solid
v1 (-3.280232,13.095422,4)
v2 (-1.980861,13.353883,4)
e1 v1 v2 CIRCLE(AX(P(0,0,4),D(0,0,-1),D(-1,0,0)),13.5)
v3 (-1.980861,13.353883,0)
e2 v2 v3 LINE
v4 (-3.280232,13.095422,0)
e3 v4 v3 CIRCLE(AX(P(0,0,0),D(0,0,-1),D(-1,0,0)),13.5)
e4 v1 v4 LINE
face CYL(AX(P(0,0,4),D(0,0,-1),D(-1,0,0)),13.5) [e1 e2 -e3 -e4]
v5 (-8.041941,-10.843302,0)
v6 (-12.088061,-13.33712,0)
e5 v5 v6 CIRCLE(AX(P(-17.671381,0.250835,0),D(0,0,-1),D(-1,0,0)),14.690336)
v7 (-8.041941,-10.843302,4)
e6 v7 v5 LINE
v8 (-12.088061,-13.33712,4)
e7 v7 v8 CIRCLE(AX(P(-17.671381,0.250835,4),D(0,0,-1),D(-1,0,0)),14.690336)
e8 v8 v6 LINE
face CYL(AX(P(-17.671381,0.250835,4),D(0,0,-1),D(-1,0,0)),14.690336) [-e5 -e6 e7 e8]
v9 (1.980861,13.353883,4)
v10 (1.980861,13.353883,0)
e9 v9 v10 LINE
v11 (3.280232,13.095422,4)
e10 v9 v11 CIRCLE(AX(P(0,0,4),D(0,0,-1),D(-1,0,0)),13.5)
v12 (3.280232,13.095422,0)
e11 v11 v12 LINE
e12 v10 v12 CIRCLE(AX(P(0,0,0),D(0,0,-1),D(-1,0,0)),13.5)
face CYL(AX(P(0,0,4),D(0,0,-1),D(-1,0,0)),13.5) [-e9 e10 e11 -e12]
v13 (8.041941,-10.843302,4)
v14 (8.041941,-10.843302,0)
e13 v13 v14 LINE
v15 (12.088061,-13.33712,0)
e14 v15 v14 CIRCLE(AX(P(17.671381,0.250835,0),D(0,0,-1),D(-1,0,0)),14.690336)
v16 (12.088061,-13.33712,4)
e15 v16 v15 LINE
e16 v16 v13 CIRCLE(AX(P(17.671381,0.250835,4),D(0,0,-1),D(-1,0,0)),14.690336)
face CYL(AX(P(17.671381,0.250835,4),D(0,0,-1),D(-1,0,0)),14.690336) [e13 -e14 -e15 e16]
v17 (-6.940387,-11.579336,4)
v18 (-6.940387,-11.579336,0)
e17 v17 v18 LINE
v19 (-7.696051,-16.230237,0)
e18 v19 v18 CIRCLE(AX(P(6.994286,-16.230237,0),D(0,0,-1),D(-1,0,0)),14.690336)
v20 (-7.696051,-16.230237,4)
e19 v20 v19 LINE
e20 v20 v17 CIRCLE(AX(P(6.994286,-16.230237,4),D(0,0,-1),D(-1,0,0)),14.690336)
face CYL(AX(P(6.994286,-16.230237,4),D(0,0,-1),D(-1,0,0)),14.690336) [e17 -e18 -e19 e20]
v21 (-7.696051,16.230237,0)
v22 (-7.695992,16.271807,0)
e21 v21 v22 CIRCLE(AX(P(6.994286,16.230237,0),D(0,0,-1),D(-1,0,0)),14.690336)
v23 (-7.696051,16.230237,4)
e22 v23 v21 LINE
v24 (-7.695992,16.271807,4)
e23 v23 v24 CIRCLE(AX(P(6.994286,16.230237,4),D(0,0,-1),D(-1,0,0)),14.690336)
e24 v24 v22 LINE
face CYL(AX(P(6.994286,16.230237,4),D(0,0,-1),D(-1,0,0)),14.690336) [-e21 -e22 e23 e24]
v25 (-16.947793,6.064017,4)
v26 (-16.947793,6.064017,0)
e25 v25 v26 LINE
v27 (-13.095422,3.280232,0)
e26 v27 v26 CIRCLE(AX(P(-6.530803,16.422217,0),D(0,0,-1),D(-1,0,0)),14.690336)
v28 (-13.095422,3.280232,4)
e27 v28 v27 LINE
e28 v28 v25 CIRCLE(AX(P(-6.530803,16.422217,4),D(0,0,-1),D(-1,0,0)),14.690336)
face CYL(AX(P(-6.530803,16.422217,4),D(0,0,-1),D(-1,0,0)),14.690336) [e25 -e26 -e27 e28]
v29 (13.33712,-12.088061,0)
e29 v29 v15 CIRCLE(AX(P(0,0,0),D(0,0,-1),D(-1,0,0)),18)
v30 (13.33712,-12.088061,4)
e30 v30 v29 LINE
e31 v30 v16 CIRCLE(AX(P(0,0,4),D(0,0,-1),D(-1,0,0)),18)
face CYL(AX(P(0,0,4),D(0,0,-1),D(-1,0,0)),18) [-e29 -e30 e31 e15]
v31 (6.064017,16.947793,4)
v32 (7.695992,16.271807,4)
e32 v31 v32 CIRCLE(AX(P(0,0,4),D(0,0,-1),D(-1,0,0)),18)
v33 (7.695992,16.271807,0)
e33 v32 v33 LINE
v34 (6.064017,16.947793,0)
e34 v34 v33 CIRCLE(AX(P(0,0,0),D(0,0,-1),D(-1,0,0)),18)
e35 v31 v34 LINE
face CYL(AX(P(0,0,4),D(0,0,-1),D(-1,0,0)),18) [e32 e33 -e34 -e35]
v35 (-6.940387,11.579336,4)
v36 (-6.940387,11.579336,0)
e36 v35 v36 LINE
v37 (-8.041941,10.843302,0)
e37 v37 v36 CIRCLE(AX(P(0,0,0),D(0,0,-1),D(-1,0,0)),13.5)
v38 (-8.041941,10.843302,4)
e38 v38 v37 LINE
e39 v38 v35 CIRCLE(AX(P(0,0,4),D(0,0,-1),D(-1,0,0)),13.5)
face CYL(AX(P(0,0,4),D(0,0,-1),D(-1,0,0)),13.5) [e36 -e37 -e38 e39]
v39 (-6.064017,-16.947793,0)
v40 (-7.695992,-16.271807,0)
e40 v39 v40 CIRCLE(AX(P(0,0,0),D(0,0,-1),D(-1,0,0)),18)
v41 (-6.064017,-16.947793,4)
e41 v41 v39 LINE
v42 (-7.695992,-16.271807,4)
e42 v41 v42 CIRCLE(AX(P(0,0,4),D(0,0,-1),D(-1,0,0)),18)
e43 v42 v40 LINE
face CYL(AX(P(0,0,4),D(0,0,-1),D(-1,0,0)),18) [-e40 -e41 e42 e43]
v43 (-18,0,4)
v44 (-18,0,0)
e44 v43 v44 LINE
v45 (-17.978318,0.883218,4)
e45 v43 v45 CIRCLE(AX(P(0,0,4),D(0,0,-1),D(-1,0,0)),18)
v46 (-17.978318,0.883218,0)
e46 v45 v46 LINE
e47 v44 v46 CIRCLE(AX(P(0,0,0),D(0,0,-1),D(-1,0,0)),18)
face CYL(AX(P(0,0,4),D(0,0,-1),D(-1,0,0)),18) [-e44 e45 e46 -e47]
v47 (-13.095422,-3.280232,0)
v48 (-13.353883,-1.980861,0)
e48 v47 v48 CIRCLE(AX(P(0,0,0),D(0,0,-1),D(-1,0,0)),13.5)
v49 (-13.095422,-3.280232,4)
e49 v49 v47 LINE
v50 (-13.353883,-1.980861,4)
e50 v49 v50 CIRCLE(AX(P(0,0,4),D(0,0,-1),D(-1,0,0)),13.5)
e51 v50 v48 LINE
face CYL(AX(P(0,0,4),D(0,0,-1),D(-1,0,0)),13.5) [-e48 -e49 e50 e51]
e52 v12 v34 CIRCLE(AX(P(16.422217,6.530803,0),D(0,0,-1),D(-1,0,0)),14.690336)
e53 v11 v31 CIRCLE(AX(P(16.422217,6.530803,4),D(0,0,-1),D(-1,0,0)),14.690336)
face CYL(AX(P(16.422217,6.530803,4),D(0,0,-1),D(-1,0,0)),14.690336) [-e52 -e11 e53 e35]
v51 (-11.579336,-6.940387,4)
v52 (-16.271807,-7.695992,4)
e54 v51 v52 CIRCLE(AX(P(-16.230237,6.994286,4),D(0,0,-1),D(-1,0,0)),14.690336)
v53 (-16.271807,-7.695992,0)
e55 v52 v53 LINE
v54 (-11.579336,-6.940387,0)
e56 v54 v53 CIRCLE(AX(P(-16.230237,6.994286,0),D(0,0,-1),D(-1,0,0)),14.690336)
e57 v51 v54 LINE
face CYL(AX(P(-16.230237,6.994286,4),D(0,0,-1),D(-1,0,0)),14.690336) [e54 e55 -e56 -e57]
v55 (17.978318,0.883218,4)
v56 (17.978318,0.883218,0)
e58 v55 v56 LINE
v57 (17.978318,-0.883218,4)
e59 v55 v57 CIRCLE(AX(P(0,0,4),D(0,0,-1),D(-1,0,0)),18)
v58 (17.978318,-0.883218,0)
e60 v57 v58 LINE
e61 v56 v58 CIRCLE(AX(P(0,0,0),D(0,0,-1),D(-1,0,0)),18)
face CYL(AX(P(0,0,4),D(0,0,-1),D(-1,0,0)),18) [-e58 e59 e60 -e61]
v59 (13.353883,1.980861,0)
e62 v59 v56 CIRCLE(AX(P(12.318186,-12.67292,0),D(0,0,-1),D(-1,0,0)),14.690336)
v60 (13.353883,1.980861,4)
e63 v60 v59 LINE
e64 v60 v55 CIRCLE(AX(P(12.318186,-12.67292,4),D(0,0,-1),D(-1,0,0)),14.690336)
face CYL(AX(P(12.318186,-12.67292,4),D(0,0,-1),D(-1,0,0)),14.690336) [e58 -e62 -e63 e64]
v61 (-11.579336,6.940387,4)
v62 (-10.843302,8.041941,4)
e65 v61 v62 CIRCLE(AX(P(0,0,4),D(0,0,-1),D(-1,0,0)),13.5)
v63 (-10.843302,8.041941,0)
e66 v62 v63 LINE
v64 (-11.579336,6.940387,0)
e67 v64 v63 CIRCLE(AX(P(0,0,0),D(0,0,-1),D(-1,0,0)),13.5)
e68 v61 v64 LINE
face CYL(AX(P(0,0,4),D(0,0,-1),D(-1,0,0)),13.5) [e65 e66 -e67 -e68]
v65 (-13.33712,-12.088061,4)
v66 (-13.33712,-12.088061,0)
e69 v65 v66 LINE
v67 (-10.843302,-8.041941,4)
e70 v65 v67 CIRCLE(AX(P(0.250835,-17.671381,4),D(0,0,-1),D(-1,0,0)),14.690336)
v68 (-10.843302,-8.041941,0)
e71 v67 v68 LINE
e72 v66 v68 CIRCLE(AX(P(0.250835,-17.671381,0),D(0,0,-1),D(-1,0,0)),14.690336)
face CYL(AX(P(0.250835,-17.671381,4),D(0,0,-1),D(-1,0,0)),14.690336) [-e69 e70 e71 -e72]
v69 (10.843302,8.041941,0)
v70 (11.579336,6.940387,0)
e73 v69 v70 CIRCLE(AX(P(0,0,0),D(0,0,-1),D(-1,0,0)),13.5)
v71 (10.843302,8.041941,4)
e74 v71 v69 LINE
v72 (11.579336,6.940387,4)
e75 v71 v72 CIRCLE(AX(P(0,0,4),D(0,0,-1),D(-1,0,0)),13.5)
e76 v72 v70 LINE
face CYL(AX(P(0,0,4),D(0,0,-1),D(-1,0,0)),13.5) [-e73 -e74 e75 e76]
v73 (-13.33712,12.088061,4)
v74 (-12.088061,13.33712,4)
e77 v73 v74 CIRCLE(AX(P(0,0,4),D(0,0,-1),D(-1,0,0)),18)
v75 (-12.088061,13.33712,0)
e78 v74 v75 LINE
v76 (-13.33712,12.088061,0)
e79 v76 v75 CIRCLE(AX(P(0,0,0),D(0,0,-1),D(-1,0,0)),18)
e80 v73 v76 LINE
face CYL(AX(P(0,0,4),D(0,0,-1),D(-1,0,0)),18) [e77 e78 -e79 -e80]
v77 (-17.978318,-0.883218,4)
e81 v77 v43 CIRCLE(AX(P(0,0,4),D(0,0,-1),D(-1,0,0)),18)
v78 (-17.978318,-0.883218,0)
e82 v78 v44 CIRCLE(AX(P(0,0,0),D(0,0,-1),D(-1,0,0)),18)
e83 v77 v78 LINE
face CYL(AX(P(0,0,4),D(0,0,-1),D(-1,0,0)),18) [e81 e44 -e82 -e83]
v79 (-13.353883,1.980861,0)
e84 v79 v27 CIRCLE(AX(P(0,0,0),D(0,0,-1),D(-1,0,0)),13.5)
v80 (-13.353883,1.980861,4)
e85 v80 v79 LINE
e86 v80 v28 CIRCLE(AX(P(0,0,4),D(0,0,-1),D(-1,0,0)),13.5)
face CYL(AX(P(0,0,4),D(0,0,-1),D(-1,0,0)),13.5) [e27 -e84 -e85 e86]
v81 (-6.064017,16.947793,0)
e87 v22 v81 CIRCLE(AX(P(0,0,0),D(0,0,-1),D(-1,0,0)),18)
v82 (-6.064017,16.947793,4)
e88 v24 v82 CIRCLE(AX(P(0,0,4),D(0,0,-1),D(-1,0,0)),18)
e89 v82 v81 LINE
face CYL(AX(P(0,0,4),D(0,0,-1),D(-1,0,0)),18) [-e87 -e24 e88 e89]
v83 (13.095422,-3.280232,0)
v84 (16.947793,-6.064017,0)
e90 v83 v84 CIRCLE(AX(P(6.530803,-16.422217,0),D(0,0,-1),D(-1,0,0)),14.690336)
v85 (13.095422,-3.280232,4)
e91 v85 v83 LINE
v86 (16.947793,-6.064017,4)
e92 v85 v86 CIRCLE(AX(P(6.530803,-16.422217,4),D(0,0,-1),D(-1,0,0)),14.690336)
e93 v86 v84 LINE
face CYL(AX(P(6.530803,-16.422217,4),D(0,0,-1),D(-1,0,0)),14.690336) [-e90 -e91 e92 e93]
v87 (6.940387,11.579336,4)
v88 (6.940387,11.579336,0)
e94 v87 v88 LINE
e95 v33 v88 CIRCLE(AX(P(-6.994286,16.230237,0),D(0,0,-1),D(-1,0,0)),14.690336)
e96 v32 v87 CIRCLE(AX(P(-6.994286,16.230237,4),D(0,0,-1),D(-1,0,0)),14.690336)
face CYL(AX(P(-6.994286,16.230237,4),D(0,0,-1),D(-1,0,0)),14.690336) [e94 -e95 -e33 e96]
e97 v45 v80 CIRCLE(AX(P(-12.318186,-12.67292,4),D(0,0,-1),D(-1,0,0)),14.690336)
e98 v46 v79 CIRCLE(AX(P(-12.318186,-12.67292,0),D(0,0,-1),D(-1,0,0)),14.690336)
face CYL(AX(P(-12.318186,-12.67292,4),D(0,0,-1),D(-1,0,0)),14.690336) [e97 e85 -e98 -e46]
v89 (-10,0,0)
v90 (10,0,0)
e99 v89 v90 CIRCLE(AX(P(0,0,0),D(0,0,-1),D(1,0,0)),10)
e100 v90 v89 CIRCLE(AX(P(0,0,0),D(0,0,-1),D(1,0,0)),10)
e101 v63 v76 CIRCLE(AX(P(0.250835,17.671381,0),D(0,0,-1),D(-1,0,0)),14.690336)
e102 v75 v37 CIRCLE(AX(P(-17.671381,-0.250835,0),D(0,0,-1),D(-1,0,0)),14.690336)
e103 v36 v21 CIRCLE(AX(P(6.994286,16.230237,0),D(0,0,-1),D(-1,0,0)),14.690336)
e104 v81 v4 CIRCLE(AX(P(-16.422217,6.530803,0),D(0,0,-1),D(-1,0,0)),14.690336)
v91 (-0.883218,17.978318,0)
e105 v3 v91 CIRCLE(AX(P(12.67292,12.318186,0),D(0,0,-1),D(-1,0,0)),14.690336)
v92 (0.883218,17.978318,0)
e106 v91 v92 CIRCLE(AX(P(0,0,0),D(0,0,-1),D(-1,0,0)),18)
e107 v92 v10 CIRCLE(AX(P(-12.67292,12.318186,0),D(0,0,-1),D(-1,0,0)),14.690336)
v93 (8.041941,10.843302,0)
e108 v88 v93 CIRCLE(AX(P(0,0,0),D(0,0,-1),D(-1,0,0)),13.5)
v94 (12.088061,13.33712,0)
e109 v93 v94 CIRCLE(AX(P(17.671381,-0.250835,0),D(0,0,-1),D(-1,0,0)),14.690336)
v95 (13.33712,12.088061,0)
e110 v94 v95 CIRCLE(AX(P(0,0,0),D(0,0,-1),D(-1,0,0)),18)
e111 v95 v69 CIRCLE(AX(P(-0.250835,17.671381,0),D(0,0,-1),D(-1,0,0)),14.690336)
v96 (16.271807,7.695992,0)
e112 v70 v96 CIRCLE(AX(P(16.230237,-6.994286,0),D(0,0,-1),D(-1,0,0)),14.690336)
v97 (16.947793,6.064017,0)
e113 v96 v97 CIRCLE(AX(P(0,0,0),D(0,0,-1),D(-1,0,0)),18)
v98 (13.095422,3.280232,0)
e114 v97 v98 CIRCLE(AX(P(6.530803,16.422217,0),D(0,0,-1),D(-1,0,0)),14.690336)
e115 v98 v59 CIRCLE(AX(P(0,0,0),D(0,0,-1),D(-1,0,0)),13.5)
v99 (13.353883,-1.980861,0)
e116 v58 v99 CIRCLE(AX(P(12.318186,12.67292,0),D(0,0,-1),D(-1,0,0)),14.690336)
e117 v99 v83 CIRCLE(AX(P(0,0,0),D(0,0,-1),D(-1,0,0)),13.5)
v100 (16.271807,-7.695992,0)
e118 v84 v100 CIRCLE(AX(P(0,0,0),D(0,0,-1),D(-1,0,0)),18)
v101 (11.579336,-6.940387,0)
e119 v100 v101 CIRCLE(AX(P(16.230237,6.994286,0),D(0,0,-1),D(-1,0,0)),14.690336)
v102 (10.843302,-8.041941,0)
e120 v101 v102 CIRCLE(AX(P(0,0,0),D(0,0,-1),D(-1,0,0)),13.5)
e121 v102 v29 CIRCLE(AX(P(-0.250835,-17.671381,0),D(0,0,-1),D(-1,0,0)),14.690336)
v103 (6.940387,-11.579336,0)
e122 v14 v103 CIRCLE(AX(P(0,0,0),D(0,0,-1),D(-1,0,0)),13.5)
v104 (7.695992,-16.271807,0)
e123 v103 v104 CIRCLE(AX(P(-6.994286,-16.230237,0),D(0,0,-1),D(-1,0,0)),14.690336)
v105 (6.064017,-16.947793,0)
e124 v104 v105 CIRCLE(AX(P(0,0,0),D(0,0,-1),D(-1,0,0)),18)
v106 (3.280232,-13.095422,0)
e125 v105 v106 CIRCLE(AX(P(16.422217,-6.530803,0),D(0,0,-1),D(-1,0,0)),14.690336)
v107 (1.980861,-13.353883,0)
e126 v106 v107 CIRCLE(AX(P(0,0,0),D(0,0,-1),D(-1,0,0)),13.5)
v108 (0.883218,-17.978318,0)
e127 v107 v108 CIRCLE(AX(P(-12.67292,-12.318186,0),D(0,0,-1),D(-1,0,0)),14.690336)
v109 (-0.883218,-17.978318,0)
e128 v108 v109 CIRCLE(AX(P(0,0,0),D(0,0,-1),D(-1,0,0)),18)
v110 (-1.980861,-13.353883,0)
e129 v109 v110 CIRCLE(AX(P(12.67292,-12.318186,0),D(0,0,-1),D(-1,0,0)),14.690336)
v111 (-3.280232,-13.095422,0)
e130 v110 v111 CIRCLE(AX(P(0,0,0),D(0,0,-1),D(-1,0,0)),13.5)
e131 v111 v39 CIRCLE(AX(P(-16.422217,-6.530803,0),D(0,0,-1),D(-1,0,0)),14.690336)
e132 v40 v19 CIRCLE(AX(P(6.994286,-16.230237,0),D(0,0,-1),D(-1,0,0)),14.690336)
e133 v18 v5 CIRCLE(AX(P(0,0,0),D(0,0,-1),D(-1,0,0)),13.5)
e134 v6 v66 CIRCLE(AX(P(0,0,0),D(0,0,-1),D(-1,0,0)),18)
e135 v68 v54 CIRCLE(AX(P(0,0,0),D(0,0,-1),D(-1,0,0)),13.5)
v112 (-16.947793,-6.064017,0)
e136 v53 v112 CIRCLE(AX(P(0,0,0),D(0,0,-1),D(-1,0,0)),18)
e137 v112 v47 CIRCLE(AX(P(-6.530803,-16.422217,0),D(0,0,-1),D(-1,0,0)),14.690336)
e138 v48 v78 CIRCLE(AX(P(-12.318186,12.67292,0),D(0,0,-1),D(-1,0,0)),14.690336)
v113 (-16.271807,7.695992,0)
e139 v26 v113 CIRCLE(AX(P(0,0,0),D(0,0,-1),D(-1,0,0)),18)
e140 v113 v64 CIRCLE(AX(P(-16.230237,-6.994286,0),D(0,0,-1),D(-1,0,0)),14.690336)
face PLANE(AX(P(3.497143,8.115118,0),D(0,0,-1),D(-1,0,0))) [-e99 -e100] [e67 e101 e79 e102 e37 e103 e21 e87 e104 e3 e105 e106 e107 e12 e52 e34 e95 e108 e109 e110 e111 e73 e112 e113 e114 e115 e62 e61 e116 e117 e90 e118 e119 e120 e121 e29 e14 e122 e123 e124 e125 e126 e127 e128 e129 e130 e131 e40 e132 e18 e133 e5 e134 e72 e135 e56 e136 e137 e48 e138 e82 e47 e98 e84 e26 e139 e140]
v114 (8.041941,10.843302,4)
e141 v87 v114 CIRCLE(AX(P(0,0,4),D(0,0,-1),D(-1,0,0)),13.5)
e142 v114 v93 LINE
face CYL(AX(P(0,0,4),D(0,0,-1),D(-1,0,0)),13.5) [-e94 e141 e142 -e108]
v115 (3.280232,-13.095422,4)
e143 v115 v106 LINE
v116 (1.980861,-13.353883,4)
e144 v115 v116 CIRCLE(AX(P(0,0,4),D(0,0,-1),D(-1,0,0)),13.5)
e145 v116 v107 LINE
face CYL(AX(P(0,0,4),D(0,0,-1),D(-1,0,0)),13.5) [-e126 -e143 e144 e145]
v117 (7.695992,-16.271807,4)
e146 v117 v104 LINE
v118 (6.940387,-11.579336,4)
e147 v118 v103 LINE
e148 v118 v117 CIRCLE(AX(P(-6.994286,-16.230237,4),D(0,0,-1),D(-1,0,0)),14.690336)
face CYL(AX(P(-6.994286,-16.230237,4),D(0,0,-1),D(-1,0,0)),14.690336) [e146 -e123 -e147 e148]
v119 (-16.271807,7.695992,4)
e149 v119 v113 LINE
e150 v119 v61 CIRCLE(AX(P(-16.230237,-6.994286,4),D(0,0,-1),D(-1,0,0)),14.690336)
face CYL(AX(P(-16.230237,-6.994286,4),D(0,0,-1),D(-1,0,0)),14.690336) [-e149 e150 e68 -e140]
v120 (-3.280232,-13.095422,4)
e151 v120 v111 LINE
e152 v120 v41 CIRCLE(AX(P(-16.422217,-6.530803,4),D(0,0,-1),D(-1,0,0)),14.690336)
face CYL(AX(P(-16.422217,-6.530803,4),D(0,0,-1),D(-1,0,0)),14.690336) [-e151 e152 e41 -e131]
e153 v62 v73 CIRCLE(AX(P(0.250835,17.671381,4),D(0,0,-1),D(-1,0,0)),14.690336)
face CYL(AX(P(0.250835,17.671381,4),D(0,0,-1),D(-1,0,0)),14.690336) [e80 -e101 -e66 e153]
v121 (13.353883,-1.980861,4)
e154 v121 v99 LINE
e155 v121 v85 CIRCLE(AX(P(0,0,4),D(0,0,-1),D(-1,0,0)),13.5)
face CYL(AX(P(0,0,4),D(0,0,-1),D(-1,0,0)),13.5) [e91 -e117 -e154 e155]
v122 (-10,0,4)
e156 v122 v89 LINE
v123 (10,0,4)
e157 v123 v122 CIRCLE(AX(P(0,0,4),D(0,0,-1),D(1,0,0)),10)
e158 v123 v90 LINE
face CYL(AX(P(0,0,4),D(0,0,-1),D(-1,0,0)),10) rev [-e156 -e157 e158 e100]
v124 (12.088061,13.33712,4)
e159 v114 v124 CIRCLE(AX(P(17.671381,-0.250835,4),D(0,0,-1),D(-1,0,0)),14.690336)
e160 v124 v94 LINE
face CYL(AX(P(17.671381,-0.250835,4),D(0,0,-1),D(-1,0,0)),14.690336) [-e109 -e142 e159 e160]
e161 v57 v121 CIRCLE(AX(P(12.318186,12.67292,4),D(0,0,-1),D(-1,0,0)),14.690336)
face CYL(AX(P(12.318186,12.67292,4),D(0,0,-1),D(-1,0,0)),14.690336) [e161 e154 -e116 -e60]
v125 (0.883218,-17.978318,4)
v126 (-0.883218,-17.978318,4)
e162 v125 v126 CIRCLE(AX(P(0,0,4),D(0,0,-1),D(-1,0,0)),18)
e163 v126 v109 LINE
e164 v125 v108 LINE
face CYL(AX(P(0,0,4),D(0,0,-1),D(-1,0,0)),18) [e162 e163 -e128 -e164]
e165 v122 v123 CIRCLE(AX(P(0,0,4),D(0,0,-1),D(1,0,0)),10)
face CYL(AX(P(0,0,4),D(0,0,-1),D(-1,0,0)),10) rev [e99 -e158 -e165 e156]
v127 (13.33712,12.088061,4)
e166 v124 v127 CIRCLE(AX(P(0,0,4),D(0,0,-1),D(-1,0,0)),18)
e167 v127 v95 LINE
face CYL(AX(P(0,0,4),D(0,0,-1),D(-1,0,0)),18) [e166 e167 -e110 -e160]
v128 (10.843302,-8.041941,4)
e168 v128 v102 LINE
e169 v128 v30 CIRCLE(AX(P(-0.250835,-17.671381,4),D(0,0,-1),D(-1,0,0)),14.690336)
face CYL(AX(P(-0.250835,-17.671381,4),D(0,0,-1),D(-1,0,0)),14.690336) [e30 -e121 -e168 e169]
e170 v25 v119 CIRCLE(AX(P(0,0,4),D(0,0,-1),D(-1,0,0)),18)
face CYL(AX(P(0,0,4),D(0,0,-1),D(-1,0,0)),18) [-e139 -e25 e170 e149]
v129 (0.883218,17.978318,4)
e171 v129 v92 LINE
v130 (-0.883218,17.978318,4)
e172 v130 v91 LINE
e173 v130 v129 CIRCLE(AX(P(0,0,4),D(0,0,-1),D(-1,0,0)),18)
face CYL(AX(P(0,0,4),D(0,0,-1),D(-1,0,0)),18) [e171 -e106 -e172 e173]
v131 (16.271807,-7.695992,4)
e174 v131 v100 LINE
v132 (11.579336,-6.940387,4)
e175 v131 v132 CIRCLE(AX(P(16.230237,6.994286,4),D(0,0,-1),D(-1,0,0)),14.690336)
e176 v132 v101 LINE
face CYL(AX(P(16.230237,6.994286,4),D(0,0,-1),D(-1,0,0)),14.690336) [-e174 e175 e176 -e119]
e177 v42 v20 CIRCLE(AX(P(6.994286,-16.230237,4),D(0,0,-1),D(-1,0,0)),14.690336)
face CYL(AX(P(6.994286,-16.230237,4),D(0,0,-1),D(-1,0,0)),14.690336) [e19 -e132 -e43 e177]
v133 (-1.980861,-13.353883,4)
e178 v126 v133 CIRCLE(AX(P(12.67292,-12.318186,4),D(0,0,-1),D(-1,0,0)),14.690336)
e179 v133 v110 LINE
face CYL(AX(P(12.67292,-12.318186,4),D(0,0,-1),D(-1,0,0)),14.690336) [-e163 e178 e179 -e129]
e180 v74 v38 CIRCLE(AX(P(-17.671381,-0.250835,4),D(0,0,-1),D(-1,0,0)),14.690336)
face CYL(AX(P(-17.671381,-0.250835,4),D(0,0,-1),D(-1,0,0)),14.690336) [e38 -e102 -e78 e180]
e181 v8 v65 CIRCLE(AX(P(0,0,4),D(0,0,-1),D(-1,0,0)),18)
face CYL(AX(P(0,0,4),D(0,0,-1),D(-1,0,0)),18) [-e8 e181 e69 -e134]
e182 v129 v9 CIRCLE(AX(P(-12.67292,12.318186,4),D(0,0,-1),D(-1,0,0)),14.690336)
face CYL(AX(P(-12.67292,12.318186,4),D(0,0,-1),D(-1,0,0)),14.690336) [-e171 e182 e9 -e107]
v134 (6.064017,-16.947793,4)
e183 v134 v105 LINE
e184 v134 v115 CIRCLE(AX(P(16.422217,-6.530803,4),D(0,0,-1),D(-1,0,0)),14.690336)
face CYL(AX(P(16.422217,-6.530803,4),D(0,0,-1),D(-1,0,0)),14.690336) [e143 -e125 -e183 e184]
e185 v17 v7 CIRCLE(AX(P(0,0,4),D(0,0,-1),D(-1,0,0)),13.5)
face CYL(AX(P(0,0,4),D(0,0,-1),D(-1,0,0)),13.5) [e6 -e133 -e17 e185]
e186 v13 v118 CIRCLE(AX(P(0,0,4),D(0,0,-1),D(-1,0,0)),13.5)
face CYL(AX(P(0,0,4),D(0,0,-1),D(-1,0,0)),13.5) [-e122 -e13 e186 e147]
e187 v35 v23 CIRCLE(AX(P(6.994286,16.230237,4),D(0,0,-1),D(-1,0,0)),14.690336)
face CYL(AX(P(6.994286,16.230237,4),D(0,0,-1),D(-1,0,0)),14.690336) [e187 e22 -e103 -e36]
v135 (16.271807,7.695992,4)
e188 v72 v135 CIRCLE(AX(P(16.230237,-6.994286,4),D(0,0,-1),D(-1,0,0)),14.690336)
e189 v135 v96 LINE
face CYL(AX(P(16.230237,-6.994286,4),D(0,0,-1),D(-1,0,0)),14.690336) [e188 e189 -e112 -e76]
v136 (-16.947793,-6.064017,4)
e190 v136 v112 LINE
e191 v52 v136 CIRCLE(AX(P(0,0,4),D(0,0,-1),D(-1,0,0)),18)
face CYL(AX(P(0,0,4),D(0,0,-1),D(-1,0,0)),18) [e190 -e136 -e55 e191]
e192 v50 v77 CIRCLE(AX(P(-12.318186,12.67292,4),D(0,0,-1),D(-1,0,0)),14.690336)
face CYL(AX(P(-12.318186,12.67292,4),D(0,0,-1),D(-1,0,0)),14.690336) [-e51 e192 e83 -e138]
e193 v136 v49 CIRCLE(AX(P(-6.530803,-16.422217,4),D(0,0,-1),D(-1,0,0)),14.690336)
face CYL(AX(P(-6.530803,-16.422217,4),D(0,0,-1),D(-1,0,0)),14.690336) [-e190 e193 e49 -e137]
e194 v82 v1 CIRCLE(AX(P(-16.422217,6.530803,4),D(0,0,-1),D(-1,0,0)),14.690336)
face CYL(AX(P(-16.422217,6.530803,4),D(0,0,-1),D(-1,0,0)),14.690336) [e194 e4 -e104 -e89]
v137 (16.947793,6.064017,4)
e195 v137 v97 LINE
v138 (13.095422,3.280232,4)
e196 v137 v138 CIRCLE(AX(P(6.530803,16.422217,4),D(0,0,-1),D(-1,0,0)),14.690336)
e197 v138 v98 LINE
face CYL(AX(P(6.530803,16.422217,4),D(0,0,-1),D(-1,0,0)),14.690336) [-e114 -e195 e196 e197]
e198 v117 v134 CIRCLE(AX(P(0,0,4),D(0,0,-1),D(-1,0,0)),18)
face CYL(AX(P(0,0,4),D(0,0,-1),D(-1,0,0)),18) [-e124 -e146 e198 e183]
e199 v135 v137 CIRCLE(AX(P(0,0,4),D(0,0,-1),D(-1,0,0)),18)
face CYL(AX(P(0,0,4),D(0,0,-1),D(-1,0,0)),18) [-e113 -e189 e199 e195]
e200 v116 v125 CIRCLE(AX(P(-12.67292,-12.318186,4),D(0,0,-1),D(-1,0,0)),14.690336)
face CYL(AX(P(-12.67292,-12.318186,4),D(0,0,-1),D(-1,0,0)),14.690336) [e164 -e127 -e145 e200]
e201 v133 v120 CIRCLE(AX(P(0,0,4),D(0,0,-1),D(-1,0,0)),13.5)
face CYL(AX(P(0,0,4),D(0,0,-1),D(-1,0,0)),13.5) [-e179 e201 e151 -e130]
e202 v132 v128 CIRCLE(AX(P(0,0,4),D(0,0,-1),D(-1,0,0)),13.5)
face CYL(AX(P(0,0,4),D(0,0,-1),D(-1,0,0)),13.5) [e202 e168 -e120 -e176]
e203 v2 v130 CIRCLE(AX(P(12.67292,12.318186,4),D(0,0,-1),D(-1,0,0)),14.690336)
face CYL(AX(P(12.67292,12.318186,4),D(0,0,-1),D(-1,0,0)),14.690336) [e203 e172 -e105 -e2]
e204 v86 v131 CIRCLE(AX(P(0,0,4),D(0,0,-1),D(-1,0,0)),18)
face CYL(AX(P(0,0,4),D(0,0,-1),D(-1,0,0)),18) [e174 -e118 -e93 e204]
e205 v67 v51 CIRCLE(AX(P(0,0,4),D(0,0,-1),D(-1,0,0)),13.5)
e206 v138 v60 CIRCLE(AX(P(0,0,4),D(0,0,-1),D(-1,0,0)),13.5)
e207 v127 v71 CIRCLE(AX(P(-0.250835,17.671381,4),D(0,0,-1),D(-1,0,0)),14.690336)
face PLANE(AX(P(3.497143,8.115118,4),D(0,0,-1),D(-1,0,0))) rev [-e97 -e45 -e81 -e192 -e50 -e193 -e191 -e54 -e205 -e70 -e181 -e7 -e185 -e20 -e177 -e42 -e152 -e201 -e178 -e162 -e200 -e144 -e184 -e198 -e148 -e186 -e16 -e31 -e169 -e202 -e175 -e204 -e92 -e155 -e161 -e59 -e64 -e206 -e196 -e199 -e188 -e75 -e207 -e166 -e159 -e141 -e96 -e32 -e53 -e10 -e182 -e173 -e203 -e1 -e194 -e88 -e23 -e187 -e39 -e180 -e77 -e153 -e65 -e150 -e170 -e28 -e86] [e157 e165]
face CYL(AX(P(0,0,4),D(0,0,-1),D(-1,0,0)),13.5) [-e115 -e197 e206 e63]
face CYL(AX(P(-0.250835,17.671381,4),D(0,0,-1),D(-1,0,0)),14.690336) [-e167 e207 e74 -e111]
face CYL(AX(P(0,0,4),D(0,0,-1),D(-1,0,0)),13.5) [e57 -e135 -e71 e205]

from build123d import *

# Parameters (mm, degrees)
SKETCH1_R           = 10
BOSS_EXTRUDE1_DEPTH = 4


with BuildPart() as part:
    # Sketch1 → Boss-Extrude1 (new body)
    with BuildSketch(Plane(origin=(0, 0, 0), x_dir=(-1, 0, 0), z_dir=(0, 0, -1))):
        with BuildLine():
            ThreePointArc((6.940387047, 11.579336235), (7.509222961, 13.894810592), (7.695991682, 16.271807276))
            ThreePointArc((7.695991682, 16.271807276), (6.888301783, 16.629831585), (6.064017361, 16.947793173))
            ThreePointArc((6.064017361, 16.947793173), (4.515292316, 15.13493727), (3.280232429, 13.095421918))
            ThreePointArc((3.280232429, 13.095421918), (2.633719347, 13.240601285), (1.980861405, 13.353882885))
            ThreePointArc((1.980861405, 13.353882885), (1.620303589, 15.710786331), (0.883218138, 17.978318212))
            ThreePointArc((0.883218138, 17.978318212), (0, 18), (-0.883218138, 17.978318212))
            ThreePointArc((-0.883218138, 17.978318212), (-1.620303589, 15.710786331), (-1.980861405, 13.353882885))
            ThreePointArc((-1.980861405, 13.353882885), (-2.633719347, 13.240601285), (-3.280232429, 13.095421918))
            ThreePointArc((-3.280232429, 13.095421918), (-4.515292316, 15.13493727), (-6.064017361, 16.947793173))
            ThreePointArc((-6.064017361, 16.947793173), (-6.888301783, 16.629831585), (-7.695991682, 16.271807276))
            ThreePointArc((-7.695991682, 16.271807276), (-7.509222961, 13.894810592), (-6.940387047, 11.579336235))
            ThreePointArc((-6.940387047, 11.579336235), (-7.500198146, 11.224839766), (-8.041940611, 10.843301675))
            ThreePointArc((-8.041940611, 10.843301675), (-9.963475897, 12.254931208), (-12.088061187, 13.337120256))
            ThreePointArc((-12.088061187, 13.337120256), (-12.727922061, 12.727922061), (-13.337120256, 12.088061187))
            ThreePointArc((-13.337120256, 12.088061187), (-12.254931208, 9.963475897), (-10.843301675, 8.041940611))
            ThreePointArc((-10.843301675, 8.041940611), (-11.224839766, 7.500198146), (-11.579336235, 6.940387047))
            ThreePointArc((-11.579336235, 6.940387047), (-13.894810592, 7.509222961), (-16.271807276, 7.695991682))
            ThreePointArc((-16.271807276, 7.695991682), (-16.629831585, 6.888301783), (-16.947793173, 6.064017361))
            ThreePointArc((-16.947793173, 6.064017361), (-15.13493727, 4.515292316), (-13.095421918, 3.280232429))
            ThreePointArc((-13.095421918, 3.280232429), (-13.240601285, 2.633719347), (-13.353882885, 1.980861405))
            ThreePointArc((-13.353882885, 1.980861405), (-15.710786331, 1.620303589), (-17.978318212, 0.883218138))
            ThreePointArc((-17.978318212, 0.883218138), (-18, 0), (-17.978318212, -0.883218138))
            ThreePointArc((-17.978318212, -0.883218138), (-15.710786331, -1.620303589), (-13.353882885, -1.980861405))
            ThreePointArc((-13.353882885, -1.980861405), (-13.240601285, -2.633719347), (-13.095421918, -3.280232429))
            ThreePointArc((-13.095421918, -3.280232429), (-15.13493727, -4.515292316), (-16.947793173, -6.064017361))
            ThreePointArc((-16.947793173, -6.064017361), (-16.629831585, -6.888301783), (-16.271807276, -7.695991682))
            ThreePointArc((-16.271807276, -7.695991682), (-13.894810592, -7.509222961), (-11.579336235, -6.940387047))
            ThreePointArc((-11.579336235, -6.940387047), (-11.224839766, -7.500198146), (-10.843301675, -8.041940611))
            ThreePointArc((-10.843301675, -8.041940611), (-12.254931208, -9.963475897), (-13.337120256, -12.088061187))
            ThreePointArc((-13.337120256, -12.088061187), (-12.727922061, -12.727922061), (-12.088061187, -13.337120256))
            ThreePointArc((-12.088061187, -13.337120256), (-9.963475897, -12.254931208), (-8.041940611, -10.843301675))
            ThreePointArc((-8.041940611, -10.843301675), (-7.500198146, -11.224839766), (-6.940387047, -11.579336235))
            ThreePointArc((-6.940387047, -11.579336235), (-7.509222961, -13.894810592), (-7.695991682, -16.271807276))
            ThreePointArc((-7.695991682, -16.271807276), (-6.888301783, -16.629831585), (-6.064017361, -16.947793173))
            ThreePointArc((-6.064017361, -16.947793173), (-4.515292316, -15.13493727), (-3.280232429, -13.095421918))
            ThreePointArc((-3.280232429, -13.095421918), (-2.633719347, -13.240601285), (-1.980861405, -13.353882885))
            ThreePointArc((-1.980861405, -13.353882885), (-1.620303589, -15.710786331), (-0.883218138, -17.978318212))
            ThreePointArc((-0.883218138, -17.978318212), (0, -18), (0.883218138, -17.978318212))
            ThreePointArc((0.883218138, -17.978318212), (1.620303589, -15.710786331), (1.980861405, -13.353882885))
            ThreePointArc((1.980861405, -13.353882885), (2.633719347, -13.240601285), (3.280232429, -13.095421918))
            ThreePointArc((3.280232429, -13.095421918), (4.515292316, -15.13493727), (6.064017361, -16.947793173))
            ThreePointArc((6.064017361, -16.947793173), (6.888301783, -16.629831585), (7.695991682, -16.271807276))
            ThreePointArc((7.695991682, -16.271807276), (7.509222961, -13.894810592), (6.940387047, -11.579336235))
            ThreePointArc((6.940387047, -11.579336235), (7.500198146, -11.224839766), (8.041940611, -10.843301675))
            ThreePointArc((8.041940611, -10.843301675), (9.963475897, -12.254931208), (12.088061187, -13.337120256))
            ThreePointArc((12.088061187, -13.337120256), (12.727922061, -12.727922061), (13.337120256, -12.088061187))
            ThreePointArc((13.337120256, -12.088061187), (12.254931208, -9.963475897), (10.843301675, -8.041940611))
            ThreePointArc((10.843301675, -8.041940611), (11.224839766, -7.500198146), (11.579336235, -6.940387047))
            ThreePointArc((11.579336235, -6.940387047), (13.894810592, -7.509222961), (16.271807276, -7.695991682))
            ThreePointArc((16.271807276, -7.695991682), (16.629831585, -6.888301783), (16.947793173, -6.064017361))
            ThreePointArc((16.947793173, -6.064017361), (15.13493727, -4.515292316), (13.095421918, -3.280232429))
            ThreePointArc((13.095421918, -3.280232429), (13.240601285, -2.633719347), (13.353882885, -1.980861405))
            ThreePointArc((13.353882885, -1.980861405), (15.710786331, -1.620303589), (17.978318212, -0.883218138))
            ThreePointArc((17.978318212, -0.883218138), (18, 0), (17.978318212, 0.883218138))
            ThreePointArc((17.978318212, 0.883218138), (15.710786331, 1.620303589), (13.353882885, 1.980861405))
            ThreePointArc((13.353882885, 1.980861405), (13.240601285, 2.633719347), (13.095421918, 3.280232429))
            ThreePointArc((13.095421918, 3.280232429), (15.13493727, 4.515292316), (16.947793173, 6.064017361))
            ThreePointArc((16.947793173, 6.064017361), (16.629831585, 6.888301783), (16.271807276, 7.695991682))
            ThreePointArc((16.271807276, 7.695991682), (13.894810592, 7.509222961), (11.579336235, 6.940387047))
            ThreePointArc((11.579336235, 6.940387047), (11.224839766, 7.500198146), (10.843301675, 8.041940611))
            ThreePointArc((10.843301675, 8.041940611), (12.254931208, 9.963475897), (13.337120256, 12.088061187))
            ThreePointArc((13.337120256, 12.088061187), (12.727922061, 12.727922061), (12.088061187, 13.337120256))
            ThreePointArc((12.088061187, 13.337120256), (9.963475897, 12.254931208), (8.041940611, 10.843301675))
            ThreePointArc((8.041940611, 10.843301675), (7.500198146, 11.224839766), (6.940387047, 11.579336235))
        make_face()
        with Locations(Location((0, 0, 0), (0, 0, 180))):
            Circle(SKETCH1_R, mode=Mode.SUBTRACT)
    extrude(amount=-BOSS_EXTRUDE1_DEPTH)


solid = part.part
